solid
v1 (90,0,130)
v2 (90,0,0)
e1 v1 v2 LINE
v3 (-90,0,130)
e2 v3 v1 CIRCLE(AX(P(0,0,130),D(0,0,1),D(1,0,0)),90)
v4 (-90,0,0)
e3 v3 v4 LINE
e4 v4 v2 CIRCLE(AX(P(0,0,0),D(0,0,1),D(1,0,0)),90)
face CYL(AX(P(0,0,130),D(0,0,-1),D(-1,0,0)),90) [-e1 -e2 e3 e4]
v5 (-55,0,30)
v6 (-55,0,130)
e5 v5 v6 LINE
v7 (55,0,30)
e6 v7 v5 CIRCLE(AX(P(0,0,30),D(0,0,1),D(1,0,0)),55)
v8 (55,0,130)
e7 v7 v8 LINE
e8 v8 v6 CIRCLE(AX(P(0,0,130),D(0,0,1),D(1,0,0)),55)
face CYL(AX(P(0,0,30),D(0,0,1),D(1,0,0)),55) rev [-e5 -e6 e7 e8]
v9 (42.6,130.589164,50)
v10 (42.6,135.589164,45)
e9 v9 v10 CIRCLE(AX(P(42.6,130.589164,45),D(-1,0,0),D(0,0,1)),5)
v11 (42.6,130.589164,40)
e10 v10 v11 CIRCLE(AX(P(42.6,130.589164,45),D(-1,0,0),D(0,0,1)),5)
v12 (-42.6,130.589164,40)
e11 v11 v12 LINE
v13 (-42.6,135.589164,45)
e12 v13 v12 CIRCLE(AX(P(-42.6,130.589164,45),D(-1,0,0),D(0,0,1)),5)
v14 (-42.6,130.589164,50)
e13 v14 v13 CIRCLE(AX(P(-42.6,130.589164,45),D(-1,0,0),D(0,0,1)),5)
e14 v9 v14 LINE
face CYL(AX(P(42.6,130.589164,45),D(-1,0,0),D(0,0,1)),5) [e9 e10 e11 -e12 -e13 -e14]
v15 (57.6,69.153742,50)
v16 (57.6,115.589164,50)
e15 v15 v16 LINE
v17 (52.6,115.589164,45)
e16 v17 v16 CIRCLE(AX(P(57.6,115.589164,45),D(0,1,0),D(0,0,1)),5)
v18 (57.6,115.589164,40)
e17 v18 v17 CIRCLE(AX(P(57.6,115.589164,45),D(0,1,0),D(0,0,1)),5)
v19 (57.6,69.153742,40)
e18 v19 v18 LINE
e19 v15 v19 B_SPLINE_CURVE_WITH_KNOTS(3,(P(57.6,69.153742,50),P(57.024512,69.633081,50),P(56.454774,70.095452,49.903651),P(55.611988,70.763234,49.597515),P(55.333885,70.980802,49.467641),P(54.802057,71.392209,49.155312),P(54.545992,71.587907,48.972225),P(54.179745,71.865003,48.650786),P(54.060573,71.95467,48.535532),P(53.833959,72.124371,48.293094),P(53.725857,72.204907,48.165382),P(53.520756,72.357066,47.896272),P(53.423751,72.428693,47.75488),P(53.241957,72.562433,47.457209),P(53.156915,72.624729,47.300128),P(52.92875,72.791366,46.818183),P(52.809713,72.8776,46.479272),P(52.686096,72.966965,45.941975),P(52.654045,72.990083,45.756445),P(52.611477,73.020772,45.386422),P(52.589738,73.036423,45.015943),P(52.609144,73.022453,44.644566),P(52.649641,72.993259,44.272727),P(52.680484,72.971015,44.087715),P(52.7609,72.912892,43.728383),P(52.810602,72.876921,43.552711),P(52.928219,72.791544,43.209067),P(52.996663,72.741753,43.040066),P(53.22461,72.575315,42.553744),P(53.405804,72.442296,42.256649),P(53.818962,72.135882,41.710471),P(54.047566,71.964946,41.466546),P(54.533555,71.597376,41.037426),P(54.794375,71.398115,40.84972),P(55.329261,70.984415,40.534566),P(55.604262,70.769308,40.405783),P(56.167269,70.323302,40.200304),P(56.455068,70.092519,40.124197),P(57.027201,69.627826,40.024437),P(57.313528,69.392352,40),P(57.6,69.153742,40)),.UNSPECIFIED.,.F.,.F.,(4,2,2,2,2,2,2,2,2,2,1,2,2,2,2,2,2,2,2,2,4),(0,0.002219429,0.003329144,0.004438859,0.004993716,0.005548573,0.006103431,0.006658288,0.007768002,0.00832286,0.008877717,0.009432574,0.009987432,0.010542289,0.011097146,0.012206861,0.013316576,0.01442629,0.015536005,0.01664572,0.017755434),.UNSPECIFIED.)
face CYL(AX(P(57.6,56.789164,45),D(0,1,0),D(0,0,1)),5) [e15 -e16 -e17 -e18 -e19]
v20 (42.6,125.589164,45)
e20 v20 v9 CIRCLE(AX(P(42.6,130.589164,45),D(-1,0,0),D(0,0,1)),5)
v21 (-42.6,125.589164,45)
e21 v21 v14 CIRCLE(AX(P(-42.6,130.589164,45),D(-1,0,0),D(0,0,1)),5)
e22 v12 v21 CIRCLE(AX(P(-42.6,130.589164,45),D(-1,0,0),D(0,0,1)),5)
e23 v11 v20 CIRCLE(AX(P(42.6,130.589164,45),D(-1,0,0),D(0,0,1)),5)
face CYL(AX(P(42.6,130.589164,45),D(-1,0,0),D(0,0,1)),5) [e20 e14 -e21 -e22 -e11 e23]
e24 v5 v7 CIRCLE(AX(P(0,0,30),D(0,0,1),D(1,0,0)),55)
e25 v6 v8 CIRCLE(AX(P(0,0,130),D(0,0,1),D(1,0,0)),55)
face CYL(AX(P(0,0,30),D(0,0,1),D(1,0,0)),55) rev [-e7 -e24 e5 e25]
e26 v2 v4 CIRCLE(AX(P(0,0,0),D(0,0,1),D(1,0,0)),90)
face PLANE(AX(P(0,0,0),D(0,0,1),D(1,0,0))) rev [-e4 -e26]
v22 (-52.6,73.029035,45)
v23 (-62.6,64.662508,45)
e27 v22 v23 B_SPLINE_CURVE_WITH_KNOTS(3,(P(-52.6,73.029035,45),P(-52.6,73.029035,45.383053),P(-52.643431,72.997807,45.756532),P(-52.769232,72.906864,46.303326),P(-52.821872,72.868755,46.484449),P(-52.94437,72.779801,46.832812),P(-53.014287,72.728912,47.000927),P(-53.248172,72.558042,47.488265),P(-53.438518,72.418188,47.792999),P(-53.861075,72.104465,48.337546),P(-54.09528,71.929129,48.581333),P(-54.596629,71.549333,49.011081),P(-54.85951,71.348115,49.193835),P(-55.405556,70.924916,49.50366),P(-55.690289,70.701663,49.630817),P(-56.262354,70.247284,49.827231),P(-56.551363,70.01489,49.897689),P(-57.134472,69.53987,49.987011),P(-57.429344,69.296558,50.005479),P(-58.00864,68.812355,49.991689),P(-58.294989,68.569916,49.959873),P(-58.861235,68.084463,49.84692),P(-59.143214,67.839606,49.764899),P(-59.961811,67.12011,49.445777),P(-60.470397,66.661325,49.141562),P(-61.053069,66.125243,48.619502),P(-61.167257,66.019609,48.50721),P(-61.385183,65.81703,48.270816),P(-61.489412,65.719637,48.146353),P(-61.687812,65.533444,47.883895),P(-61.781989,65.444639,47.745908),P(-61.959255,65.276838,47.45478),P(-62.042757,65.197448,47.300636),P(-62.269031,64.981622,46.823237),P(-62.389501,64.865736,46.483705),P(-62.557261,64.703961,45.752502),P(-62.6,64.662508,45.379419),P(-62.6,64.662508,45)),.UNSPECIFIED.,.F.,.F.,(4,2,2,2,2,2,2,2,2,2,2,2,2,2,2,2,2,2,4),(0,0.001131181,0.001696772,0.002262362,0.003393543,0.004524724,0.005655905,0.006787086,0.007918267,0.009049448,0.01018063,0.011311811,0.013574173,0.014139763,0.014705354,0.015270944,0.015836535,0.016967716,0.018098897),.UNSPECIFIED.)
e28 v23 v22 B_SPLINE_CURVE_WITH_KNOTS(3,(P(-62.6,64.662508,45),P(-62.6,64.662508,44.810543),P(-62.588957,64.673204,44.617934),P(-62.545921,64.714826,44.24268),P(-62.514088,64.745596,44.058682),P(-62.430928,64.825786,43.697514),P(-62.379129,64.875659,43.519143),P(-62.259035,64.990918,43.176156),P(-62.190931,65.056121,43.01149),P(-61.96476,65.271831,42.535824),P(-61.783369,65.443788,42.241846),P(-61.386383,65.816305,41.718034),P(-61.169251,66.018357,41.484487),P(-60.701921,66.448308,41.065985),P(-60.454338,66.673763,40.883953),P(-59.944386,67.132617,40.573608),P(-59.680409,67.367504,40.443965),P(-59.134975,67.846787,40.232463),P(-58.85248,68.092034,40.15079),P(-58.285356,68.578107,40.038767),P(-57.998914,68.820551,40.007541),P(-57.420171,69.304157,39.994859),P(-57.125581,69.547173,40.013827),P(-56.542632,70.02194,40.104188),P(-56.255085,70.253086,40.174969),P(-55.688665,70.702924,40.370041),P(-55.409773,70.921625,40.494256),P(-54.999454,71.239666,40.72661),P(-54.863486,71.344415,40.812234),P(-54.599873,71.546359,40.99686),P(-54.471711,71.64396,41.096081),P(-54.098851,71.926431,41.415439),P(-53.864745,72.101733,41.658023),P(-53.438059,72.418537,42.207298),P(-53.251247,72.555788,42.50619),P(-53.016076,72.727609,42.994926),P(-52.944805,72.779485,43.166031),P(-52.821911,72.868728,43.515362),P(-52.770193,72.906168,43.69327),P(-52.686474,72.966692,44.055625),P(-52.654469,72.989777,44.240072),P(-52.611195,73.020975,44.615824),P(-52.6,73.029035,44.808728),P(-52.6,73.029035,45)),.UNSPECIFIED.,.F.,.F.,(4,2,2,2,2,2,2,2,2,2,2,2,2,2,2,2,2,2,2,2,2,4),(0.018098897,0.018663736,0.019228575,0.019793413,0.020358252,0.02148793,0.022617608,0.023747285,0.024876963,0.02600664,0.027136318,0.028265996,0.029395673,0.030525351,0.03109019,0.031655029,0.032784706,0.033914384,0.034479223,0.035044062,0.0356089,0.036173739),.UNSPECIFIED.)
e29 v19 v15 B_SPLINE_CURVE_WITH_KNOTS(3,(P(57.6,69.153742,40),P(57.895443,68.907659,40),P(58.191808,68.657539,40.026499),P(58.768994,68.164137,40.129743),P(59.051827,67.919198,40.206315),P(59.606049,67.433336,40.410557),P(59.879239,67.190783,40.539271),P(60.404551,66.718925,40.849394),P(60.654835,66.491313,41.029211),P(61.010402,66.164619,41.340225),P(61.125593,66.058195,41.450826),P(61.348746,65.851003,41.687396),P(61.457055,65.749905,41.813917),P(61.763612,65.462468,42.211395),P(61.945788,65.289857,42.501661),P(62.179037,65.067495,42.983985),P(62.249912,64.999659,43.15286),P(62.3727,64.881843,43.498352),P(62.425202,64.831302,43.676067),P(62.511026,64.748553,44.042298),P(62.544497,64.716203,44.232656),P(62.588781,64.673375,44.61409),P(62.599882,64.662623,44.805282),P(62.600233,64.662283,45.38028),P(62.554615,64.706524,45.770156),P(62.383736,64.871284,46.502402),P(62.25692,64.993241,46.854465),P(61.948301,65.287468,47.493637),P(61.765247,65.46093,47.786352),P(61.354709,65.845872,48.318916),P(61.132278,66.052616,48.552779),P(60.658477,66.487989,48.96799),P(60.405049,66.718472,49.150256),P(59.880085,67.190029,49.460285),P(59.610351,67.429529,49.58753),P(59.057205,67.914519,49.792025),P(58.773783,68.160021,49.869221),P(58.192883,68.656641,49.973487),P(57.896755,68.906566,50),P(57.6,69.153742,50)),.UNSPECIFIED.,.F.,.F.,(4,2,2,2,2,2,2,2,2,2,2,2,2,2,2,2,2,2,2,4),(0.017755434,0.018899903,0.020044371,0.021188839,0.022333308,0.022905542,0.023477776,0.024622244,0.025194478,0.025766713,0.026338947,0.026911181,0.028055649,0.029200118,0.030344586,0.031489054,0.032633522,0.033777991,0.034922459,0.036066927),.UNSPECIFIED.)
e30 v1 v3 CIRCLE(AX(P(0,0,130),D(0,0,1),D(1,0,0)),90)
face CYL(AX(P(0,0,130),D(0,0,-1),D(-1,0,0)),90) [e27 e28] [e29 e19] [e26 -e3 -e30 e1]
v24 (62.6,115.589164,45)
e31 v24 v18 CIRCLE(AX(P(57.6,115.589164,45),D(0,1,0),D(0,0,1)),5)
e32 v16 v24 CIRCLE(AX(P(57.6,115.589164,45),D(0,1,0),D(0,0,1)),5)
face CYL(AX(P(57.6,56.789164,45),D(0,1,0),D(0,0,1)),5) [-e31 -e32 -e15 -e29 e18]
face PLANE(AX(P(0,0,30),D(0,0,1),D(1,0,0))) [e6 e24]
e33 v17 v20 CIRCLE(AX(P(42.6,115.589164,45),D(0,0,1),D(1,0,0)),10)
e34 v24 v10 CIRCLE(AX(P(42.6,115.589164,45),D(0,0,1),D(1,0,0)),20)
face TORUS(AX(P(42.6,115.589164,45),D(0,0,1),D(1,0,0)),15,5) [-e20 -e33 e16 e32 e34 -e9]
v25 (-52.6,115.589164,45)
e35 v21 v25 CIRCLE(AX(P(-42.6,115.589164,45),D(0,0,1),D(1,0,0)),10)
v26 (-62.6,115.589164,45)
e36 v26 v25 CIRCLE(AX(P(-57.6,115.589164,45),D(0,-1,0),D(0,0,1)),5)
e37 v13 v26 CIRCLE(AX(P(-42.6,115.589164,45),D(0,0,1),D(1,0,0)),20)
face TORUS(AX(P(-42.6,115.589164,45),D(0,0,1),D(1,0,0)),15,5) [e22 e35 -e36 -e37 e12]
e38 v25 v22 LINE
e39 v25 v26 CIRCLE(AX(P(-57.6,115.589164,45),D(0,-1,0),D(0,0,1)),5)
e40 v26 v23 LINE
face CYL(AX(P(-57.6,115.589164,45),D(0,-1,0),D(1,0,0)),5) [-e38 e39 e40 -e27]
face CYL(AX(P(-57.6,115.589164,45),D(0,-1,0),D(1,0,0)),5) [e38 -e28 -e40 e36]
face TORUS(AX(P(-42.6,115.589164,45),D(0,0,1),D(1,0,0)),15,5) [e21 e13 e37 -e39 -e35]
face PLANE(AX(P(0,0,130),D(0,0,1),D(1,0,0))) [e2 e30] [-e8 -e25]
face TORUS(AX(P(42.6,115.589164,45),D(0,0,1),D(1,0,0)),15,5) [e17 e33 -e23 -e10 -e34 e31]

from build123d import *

# Parameters (mm, degrees)
SKETCH1_R           = 90
BOSS_EXTRUDE1_DEPTH = 130
SKETCH2_R           = 55
CUT_EXTRUDE1_DEPTH  = 100
SWEEP1_PROFILE_R    = 5


with BuildPart() as part:
    # Sketch1 → Boss-Extrude1 (new body)
    with BuildSketch(Plane.XY):
        Circle(SKETCH1_R)
    extrude(amount=BOSS_EXTRUDE1_DEPTH)

    # Sketch2 → Cut-Extrude1 (cut)
    with BuildSketch(Plane.XY.offset(130)):
        Circle(SKETCH2_R)
    extrude(amount=-CUT_EXTRUDE1_DEPTH, mode=Mode.SUBTRACT)

    # Sweep1: sweep along a path in Sketch3
    with BuildLine(Plane(origin=(0, 0, 45), x_dir=(-1, 0, 0), z_dir=(0, 0, -1))) as sweep1_path:
        Line((-57.6, 56.789164475), (-57.6, 115.589164475))
        ThreePointArc((-57.6, 115.589164475), (-53.206601718, 126.195766193), (-42.6, 130.589164475))
        Line((-42.6, 130.589164475), (42.6, 130.589164475))
        ThreePointArc((42.6, 130.589164475), (53.206601718, 126.195766193), (57.6, 115.589164475))
        Line((57.6, 115.589164475), (57.6, 56.789164475))
    # Sweep1 profile (on start of the path) → Sweep1 (sweep)
    with BuildSketch(Plane(origin=(57.6, 56.789164475, 45), x_dir=(0, 0, 1), z_dir=(0, 1, 0))):
        Circle(SWEEP1_PROFILE_R)
    sweep(path=sweep1_path.line)


solid = part.part
